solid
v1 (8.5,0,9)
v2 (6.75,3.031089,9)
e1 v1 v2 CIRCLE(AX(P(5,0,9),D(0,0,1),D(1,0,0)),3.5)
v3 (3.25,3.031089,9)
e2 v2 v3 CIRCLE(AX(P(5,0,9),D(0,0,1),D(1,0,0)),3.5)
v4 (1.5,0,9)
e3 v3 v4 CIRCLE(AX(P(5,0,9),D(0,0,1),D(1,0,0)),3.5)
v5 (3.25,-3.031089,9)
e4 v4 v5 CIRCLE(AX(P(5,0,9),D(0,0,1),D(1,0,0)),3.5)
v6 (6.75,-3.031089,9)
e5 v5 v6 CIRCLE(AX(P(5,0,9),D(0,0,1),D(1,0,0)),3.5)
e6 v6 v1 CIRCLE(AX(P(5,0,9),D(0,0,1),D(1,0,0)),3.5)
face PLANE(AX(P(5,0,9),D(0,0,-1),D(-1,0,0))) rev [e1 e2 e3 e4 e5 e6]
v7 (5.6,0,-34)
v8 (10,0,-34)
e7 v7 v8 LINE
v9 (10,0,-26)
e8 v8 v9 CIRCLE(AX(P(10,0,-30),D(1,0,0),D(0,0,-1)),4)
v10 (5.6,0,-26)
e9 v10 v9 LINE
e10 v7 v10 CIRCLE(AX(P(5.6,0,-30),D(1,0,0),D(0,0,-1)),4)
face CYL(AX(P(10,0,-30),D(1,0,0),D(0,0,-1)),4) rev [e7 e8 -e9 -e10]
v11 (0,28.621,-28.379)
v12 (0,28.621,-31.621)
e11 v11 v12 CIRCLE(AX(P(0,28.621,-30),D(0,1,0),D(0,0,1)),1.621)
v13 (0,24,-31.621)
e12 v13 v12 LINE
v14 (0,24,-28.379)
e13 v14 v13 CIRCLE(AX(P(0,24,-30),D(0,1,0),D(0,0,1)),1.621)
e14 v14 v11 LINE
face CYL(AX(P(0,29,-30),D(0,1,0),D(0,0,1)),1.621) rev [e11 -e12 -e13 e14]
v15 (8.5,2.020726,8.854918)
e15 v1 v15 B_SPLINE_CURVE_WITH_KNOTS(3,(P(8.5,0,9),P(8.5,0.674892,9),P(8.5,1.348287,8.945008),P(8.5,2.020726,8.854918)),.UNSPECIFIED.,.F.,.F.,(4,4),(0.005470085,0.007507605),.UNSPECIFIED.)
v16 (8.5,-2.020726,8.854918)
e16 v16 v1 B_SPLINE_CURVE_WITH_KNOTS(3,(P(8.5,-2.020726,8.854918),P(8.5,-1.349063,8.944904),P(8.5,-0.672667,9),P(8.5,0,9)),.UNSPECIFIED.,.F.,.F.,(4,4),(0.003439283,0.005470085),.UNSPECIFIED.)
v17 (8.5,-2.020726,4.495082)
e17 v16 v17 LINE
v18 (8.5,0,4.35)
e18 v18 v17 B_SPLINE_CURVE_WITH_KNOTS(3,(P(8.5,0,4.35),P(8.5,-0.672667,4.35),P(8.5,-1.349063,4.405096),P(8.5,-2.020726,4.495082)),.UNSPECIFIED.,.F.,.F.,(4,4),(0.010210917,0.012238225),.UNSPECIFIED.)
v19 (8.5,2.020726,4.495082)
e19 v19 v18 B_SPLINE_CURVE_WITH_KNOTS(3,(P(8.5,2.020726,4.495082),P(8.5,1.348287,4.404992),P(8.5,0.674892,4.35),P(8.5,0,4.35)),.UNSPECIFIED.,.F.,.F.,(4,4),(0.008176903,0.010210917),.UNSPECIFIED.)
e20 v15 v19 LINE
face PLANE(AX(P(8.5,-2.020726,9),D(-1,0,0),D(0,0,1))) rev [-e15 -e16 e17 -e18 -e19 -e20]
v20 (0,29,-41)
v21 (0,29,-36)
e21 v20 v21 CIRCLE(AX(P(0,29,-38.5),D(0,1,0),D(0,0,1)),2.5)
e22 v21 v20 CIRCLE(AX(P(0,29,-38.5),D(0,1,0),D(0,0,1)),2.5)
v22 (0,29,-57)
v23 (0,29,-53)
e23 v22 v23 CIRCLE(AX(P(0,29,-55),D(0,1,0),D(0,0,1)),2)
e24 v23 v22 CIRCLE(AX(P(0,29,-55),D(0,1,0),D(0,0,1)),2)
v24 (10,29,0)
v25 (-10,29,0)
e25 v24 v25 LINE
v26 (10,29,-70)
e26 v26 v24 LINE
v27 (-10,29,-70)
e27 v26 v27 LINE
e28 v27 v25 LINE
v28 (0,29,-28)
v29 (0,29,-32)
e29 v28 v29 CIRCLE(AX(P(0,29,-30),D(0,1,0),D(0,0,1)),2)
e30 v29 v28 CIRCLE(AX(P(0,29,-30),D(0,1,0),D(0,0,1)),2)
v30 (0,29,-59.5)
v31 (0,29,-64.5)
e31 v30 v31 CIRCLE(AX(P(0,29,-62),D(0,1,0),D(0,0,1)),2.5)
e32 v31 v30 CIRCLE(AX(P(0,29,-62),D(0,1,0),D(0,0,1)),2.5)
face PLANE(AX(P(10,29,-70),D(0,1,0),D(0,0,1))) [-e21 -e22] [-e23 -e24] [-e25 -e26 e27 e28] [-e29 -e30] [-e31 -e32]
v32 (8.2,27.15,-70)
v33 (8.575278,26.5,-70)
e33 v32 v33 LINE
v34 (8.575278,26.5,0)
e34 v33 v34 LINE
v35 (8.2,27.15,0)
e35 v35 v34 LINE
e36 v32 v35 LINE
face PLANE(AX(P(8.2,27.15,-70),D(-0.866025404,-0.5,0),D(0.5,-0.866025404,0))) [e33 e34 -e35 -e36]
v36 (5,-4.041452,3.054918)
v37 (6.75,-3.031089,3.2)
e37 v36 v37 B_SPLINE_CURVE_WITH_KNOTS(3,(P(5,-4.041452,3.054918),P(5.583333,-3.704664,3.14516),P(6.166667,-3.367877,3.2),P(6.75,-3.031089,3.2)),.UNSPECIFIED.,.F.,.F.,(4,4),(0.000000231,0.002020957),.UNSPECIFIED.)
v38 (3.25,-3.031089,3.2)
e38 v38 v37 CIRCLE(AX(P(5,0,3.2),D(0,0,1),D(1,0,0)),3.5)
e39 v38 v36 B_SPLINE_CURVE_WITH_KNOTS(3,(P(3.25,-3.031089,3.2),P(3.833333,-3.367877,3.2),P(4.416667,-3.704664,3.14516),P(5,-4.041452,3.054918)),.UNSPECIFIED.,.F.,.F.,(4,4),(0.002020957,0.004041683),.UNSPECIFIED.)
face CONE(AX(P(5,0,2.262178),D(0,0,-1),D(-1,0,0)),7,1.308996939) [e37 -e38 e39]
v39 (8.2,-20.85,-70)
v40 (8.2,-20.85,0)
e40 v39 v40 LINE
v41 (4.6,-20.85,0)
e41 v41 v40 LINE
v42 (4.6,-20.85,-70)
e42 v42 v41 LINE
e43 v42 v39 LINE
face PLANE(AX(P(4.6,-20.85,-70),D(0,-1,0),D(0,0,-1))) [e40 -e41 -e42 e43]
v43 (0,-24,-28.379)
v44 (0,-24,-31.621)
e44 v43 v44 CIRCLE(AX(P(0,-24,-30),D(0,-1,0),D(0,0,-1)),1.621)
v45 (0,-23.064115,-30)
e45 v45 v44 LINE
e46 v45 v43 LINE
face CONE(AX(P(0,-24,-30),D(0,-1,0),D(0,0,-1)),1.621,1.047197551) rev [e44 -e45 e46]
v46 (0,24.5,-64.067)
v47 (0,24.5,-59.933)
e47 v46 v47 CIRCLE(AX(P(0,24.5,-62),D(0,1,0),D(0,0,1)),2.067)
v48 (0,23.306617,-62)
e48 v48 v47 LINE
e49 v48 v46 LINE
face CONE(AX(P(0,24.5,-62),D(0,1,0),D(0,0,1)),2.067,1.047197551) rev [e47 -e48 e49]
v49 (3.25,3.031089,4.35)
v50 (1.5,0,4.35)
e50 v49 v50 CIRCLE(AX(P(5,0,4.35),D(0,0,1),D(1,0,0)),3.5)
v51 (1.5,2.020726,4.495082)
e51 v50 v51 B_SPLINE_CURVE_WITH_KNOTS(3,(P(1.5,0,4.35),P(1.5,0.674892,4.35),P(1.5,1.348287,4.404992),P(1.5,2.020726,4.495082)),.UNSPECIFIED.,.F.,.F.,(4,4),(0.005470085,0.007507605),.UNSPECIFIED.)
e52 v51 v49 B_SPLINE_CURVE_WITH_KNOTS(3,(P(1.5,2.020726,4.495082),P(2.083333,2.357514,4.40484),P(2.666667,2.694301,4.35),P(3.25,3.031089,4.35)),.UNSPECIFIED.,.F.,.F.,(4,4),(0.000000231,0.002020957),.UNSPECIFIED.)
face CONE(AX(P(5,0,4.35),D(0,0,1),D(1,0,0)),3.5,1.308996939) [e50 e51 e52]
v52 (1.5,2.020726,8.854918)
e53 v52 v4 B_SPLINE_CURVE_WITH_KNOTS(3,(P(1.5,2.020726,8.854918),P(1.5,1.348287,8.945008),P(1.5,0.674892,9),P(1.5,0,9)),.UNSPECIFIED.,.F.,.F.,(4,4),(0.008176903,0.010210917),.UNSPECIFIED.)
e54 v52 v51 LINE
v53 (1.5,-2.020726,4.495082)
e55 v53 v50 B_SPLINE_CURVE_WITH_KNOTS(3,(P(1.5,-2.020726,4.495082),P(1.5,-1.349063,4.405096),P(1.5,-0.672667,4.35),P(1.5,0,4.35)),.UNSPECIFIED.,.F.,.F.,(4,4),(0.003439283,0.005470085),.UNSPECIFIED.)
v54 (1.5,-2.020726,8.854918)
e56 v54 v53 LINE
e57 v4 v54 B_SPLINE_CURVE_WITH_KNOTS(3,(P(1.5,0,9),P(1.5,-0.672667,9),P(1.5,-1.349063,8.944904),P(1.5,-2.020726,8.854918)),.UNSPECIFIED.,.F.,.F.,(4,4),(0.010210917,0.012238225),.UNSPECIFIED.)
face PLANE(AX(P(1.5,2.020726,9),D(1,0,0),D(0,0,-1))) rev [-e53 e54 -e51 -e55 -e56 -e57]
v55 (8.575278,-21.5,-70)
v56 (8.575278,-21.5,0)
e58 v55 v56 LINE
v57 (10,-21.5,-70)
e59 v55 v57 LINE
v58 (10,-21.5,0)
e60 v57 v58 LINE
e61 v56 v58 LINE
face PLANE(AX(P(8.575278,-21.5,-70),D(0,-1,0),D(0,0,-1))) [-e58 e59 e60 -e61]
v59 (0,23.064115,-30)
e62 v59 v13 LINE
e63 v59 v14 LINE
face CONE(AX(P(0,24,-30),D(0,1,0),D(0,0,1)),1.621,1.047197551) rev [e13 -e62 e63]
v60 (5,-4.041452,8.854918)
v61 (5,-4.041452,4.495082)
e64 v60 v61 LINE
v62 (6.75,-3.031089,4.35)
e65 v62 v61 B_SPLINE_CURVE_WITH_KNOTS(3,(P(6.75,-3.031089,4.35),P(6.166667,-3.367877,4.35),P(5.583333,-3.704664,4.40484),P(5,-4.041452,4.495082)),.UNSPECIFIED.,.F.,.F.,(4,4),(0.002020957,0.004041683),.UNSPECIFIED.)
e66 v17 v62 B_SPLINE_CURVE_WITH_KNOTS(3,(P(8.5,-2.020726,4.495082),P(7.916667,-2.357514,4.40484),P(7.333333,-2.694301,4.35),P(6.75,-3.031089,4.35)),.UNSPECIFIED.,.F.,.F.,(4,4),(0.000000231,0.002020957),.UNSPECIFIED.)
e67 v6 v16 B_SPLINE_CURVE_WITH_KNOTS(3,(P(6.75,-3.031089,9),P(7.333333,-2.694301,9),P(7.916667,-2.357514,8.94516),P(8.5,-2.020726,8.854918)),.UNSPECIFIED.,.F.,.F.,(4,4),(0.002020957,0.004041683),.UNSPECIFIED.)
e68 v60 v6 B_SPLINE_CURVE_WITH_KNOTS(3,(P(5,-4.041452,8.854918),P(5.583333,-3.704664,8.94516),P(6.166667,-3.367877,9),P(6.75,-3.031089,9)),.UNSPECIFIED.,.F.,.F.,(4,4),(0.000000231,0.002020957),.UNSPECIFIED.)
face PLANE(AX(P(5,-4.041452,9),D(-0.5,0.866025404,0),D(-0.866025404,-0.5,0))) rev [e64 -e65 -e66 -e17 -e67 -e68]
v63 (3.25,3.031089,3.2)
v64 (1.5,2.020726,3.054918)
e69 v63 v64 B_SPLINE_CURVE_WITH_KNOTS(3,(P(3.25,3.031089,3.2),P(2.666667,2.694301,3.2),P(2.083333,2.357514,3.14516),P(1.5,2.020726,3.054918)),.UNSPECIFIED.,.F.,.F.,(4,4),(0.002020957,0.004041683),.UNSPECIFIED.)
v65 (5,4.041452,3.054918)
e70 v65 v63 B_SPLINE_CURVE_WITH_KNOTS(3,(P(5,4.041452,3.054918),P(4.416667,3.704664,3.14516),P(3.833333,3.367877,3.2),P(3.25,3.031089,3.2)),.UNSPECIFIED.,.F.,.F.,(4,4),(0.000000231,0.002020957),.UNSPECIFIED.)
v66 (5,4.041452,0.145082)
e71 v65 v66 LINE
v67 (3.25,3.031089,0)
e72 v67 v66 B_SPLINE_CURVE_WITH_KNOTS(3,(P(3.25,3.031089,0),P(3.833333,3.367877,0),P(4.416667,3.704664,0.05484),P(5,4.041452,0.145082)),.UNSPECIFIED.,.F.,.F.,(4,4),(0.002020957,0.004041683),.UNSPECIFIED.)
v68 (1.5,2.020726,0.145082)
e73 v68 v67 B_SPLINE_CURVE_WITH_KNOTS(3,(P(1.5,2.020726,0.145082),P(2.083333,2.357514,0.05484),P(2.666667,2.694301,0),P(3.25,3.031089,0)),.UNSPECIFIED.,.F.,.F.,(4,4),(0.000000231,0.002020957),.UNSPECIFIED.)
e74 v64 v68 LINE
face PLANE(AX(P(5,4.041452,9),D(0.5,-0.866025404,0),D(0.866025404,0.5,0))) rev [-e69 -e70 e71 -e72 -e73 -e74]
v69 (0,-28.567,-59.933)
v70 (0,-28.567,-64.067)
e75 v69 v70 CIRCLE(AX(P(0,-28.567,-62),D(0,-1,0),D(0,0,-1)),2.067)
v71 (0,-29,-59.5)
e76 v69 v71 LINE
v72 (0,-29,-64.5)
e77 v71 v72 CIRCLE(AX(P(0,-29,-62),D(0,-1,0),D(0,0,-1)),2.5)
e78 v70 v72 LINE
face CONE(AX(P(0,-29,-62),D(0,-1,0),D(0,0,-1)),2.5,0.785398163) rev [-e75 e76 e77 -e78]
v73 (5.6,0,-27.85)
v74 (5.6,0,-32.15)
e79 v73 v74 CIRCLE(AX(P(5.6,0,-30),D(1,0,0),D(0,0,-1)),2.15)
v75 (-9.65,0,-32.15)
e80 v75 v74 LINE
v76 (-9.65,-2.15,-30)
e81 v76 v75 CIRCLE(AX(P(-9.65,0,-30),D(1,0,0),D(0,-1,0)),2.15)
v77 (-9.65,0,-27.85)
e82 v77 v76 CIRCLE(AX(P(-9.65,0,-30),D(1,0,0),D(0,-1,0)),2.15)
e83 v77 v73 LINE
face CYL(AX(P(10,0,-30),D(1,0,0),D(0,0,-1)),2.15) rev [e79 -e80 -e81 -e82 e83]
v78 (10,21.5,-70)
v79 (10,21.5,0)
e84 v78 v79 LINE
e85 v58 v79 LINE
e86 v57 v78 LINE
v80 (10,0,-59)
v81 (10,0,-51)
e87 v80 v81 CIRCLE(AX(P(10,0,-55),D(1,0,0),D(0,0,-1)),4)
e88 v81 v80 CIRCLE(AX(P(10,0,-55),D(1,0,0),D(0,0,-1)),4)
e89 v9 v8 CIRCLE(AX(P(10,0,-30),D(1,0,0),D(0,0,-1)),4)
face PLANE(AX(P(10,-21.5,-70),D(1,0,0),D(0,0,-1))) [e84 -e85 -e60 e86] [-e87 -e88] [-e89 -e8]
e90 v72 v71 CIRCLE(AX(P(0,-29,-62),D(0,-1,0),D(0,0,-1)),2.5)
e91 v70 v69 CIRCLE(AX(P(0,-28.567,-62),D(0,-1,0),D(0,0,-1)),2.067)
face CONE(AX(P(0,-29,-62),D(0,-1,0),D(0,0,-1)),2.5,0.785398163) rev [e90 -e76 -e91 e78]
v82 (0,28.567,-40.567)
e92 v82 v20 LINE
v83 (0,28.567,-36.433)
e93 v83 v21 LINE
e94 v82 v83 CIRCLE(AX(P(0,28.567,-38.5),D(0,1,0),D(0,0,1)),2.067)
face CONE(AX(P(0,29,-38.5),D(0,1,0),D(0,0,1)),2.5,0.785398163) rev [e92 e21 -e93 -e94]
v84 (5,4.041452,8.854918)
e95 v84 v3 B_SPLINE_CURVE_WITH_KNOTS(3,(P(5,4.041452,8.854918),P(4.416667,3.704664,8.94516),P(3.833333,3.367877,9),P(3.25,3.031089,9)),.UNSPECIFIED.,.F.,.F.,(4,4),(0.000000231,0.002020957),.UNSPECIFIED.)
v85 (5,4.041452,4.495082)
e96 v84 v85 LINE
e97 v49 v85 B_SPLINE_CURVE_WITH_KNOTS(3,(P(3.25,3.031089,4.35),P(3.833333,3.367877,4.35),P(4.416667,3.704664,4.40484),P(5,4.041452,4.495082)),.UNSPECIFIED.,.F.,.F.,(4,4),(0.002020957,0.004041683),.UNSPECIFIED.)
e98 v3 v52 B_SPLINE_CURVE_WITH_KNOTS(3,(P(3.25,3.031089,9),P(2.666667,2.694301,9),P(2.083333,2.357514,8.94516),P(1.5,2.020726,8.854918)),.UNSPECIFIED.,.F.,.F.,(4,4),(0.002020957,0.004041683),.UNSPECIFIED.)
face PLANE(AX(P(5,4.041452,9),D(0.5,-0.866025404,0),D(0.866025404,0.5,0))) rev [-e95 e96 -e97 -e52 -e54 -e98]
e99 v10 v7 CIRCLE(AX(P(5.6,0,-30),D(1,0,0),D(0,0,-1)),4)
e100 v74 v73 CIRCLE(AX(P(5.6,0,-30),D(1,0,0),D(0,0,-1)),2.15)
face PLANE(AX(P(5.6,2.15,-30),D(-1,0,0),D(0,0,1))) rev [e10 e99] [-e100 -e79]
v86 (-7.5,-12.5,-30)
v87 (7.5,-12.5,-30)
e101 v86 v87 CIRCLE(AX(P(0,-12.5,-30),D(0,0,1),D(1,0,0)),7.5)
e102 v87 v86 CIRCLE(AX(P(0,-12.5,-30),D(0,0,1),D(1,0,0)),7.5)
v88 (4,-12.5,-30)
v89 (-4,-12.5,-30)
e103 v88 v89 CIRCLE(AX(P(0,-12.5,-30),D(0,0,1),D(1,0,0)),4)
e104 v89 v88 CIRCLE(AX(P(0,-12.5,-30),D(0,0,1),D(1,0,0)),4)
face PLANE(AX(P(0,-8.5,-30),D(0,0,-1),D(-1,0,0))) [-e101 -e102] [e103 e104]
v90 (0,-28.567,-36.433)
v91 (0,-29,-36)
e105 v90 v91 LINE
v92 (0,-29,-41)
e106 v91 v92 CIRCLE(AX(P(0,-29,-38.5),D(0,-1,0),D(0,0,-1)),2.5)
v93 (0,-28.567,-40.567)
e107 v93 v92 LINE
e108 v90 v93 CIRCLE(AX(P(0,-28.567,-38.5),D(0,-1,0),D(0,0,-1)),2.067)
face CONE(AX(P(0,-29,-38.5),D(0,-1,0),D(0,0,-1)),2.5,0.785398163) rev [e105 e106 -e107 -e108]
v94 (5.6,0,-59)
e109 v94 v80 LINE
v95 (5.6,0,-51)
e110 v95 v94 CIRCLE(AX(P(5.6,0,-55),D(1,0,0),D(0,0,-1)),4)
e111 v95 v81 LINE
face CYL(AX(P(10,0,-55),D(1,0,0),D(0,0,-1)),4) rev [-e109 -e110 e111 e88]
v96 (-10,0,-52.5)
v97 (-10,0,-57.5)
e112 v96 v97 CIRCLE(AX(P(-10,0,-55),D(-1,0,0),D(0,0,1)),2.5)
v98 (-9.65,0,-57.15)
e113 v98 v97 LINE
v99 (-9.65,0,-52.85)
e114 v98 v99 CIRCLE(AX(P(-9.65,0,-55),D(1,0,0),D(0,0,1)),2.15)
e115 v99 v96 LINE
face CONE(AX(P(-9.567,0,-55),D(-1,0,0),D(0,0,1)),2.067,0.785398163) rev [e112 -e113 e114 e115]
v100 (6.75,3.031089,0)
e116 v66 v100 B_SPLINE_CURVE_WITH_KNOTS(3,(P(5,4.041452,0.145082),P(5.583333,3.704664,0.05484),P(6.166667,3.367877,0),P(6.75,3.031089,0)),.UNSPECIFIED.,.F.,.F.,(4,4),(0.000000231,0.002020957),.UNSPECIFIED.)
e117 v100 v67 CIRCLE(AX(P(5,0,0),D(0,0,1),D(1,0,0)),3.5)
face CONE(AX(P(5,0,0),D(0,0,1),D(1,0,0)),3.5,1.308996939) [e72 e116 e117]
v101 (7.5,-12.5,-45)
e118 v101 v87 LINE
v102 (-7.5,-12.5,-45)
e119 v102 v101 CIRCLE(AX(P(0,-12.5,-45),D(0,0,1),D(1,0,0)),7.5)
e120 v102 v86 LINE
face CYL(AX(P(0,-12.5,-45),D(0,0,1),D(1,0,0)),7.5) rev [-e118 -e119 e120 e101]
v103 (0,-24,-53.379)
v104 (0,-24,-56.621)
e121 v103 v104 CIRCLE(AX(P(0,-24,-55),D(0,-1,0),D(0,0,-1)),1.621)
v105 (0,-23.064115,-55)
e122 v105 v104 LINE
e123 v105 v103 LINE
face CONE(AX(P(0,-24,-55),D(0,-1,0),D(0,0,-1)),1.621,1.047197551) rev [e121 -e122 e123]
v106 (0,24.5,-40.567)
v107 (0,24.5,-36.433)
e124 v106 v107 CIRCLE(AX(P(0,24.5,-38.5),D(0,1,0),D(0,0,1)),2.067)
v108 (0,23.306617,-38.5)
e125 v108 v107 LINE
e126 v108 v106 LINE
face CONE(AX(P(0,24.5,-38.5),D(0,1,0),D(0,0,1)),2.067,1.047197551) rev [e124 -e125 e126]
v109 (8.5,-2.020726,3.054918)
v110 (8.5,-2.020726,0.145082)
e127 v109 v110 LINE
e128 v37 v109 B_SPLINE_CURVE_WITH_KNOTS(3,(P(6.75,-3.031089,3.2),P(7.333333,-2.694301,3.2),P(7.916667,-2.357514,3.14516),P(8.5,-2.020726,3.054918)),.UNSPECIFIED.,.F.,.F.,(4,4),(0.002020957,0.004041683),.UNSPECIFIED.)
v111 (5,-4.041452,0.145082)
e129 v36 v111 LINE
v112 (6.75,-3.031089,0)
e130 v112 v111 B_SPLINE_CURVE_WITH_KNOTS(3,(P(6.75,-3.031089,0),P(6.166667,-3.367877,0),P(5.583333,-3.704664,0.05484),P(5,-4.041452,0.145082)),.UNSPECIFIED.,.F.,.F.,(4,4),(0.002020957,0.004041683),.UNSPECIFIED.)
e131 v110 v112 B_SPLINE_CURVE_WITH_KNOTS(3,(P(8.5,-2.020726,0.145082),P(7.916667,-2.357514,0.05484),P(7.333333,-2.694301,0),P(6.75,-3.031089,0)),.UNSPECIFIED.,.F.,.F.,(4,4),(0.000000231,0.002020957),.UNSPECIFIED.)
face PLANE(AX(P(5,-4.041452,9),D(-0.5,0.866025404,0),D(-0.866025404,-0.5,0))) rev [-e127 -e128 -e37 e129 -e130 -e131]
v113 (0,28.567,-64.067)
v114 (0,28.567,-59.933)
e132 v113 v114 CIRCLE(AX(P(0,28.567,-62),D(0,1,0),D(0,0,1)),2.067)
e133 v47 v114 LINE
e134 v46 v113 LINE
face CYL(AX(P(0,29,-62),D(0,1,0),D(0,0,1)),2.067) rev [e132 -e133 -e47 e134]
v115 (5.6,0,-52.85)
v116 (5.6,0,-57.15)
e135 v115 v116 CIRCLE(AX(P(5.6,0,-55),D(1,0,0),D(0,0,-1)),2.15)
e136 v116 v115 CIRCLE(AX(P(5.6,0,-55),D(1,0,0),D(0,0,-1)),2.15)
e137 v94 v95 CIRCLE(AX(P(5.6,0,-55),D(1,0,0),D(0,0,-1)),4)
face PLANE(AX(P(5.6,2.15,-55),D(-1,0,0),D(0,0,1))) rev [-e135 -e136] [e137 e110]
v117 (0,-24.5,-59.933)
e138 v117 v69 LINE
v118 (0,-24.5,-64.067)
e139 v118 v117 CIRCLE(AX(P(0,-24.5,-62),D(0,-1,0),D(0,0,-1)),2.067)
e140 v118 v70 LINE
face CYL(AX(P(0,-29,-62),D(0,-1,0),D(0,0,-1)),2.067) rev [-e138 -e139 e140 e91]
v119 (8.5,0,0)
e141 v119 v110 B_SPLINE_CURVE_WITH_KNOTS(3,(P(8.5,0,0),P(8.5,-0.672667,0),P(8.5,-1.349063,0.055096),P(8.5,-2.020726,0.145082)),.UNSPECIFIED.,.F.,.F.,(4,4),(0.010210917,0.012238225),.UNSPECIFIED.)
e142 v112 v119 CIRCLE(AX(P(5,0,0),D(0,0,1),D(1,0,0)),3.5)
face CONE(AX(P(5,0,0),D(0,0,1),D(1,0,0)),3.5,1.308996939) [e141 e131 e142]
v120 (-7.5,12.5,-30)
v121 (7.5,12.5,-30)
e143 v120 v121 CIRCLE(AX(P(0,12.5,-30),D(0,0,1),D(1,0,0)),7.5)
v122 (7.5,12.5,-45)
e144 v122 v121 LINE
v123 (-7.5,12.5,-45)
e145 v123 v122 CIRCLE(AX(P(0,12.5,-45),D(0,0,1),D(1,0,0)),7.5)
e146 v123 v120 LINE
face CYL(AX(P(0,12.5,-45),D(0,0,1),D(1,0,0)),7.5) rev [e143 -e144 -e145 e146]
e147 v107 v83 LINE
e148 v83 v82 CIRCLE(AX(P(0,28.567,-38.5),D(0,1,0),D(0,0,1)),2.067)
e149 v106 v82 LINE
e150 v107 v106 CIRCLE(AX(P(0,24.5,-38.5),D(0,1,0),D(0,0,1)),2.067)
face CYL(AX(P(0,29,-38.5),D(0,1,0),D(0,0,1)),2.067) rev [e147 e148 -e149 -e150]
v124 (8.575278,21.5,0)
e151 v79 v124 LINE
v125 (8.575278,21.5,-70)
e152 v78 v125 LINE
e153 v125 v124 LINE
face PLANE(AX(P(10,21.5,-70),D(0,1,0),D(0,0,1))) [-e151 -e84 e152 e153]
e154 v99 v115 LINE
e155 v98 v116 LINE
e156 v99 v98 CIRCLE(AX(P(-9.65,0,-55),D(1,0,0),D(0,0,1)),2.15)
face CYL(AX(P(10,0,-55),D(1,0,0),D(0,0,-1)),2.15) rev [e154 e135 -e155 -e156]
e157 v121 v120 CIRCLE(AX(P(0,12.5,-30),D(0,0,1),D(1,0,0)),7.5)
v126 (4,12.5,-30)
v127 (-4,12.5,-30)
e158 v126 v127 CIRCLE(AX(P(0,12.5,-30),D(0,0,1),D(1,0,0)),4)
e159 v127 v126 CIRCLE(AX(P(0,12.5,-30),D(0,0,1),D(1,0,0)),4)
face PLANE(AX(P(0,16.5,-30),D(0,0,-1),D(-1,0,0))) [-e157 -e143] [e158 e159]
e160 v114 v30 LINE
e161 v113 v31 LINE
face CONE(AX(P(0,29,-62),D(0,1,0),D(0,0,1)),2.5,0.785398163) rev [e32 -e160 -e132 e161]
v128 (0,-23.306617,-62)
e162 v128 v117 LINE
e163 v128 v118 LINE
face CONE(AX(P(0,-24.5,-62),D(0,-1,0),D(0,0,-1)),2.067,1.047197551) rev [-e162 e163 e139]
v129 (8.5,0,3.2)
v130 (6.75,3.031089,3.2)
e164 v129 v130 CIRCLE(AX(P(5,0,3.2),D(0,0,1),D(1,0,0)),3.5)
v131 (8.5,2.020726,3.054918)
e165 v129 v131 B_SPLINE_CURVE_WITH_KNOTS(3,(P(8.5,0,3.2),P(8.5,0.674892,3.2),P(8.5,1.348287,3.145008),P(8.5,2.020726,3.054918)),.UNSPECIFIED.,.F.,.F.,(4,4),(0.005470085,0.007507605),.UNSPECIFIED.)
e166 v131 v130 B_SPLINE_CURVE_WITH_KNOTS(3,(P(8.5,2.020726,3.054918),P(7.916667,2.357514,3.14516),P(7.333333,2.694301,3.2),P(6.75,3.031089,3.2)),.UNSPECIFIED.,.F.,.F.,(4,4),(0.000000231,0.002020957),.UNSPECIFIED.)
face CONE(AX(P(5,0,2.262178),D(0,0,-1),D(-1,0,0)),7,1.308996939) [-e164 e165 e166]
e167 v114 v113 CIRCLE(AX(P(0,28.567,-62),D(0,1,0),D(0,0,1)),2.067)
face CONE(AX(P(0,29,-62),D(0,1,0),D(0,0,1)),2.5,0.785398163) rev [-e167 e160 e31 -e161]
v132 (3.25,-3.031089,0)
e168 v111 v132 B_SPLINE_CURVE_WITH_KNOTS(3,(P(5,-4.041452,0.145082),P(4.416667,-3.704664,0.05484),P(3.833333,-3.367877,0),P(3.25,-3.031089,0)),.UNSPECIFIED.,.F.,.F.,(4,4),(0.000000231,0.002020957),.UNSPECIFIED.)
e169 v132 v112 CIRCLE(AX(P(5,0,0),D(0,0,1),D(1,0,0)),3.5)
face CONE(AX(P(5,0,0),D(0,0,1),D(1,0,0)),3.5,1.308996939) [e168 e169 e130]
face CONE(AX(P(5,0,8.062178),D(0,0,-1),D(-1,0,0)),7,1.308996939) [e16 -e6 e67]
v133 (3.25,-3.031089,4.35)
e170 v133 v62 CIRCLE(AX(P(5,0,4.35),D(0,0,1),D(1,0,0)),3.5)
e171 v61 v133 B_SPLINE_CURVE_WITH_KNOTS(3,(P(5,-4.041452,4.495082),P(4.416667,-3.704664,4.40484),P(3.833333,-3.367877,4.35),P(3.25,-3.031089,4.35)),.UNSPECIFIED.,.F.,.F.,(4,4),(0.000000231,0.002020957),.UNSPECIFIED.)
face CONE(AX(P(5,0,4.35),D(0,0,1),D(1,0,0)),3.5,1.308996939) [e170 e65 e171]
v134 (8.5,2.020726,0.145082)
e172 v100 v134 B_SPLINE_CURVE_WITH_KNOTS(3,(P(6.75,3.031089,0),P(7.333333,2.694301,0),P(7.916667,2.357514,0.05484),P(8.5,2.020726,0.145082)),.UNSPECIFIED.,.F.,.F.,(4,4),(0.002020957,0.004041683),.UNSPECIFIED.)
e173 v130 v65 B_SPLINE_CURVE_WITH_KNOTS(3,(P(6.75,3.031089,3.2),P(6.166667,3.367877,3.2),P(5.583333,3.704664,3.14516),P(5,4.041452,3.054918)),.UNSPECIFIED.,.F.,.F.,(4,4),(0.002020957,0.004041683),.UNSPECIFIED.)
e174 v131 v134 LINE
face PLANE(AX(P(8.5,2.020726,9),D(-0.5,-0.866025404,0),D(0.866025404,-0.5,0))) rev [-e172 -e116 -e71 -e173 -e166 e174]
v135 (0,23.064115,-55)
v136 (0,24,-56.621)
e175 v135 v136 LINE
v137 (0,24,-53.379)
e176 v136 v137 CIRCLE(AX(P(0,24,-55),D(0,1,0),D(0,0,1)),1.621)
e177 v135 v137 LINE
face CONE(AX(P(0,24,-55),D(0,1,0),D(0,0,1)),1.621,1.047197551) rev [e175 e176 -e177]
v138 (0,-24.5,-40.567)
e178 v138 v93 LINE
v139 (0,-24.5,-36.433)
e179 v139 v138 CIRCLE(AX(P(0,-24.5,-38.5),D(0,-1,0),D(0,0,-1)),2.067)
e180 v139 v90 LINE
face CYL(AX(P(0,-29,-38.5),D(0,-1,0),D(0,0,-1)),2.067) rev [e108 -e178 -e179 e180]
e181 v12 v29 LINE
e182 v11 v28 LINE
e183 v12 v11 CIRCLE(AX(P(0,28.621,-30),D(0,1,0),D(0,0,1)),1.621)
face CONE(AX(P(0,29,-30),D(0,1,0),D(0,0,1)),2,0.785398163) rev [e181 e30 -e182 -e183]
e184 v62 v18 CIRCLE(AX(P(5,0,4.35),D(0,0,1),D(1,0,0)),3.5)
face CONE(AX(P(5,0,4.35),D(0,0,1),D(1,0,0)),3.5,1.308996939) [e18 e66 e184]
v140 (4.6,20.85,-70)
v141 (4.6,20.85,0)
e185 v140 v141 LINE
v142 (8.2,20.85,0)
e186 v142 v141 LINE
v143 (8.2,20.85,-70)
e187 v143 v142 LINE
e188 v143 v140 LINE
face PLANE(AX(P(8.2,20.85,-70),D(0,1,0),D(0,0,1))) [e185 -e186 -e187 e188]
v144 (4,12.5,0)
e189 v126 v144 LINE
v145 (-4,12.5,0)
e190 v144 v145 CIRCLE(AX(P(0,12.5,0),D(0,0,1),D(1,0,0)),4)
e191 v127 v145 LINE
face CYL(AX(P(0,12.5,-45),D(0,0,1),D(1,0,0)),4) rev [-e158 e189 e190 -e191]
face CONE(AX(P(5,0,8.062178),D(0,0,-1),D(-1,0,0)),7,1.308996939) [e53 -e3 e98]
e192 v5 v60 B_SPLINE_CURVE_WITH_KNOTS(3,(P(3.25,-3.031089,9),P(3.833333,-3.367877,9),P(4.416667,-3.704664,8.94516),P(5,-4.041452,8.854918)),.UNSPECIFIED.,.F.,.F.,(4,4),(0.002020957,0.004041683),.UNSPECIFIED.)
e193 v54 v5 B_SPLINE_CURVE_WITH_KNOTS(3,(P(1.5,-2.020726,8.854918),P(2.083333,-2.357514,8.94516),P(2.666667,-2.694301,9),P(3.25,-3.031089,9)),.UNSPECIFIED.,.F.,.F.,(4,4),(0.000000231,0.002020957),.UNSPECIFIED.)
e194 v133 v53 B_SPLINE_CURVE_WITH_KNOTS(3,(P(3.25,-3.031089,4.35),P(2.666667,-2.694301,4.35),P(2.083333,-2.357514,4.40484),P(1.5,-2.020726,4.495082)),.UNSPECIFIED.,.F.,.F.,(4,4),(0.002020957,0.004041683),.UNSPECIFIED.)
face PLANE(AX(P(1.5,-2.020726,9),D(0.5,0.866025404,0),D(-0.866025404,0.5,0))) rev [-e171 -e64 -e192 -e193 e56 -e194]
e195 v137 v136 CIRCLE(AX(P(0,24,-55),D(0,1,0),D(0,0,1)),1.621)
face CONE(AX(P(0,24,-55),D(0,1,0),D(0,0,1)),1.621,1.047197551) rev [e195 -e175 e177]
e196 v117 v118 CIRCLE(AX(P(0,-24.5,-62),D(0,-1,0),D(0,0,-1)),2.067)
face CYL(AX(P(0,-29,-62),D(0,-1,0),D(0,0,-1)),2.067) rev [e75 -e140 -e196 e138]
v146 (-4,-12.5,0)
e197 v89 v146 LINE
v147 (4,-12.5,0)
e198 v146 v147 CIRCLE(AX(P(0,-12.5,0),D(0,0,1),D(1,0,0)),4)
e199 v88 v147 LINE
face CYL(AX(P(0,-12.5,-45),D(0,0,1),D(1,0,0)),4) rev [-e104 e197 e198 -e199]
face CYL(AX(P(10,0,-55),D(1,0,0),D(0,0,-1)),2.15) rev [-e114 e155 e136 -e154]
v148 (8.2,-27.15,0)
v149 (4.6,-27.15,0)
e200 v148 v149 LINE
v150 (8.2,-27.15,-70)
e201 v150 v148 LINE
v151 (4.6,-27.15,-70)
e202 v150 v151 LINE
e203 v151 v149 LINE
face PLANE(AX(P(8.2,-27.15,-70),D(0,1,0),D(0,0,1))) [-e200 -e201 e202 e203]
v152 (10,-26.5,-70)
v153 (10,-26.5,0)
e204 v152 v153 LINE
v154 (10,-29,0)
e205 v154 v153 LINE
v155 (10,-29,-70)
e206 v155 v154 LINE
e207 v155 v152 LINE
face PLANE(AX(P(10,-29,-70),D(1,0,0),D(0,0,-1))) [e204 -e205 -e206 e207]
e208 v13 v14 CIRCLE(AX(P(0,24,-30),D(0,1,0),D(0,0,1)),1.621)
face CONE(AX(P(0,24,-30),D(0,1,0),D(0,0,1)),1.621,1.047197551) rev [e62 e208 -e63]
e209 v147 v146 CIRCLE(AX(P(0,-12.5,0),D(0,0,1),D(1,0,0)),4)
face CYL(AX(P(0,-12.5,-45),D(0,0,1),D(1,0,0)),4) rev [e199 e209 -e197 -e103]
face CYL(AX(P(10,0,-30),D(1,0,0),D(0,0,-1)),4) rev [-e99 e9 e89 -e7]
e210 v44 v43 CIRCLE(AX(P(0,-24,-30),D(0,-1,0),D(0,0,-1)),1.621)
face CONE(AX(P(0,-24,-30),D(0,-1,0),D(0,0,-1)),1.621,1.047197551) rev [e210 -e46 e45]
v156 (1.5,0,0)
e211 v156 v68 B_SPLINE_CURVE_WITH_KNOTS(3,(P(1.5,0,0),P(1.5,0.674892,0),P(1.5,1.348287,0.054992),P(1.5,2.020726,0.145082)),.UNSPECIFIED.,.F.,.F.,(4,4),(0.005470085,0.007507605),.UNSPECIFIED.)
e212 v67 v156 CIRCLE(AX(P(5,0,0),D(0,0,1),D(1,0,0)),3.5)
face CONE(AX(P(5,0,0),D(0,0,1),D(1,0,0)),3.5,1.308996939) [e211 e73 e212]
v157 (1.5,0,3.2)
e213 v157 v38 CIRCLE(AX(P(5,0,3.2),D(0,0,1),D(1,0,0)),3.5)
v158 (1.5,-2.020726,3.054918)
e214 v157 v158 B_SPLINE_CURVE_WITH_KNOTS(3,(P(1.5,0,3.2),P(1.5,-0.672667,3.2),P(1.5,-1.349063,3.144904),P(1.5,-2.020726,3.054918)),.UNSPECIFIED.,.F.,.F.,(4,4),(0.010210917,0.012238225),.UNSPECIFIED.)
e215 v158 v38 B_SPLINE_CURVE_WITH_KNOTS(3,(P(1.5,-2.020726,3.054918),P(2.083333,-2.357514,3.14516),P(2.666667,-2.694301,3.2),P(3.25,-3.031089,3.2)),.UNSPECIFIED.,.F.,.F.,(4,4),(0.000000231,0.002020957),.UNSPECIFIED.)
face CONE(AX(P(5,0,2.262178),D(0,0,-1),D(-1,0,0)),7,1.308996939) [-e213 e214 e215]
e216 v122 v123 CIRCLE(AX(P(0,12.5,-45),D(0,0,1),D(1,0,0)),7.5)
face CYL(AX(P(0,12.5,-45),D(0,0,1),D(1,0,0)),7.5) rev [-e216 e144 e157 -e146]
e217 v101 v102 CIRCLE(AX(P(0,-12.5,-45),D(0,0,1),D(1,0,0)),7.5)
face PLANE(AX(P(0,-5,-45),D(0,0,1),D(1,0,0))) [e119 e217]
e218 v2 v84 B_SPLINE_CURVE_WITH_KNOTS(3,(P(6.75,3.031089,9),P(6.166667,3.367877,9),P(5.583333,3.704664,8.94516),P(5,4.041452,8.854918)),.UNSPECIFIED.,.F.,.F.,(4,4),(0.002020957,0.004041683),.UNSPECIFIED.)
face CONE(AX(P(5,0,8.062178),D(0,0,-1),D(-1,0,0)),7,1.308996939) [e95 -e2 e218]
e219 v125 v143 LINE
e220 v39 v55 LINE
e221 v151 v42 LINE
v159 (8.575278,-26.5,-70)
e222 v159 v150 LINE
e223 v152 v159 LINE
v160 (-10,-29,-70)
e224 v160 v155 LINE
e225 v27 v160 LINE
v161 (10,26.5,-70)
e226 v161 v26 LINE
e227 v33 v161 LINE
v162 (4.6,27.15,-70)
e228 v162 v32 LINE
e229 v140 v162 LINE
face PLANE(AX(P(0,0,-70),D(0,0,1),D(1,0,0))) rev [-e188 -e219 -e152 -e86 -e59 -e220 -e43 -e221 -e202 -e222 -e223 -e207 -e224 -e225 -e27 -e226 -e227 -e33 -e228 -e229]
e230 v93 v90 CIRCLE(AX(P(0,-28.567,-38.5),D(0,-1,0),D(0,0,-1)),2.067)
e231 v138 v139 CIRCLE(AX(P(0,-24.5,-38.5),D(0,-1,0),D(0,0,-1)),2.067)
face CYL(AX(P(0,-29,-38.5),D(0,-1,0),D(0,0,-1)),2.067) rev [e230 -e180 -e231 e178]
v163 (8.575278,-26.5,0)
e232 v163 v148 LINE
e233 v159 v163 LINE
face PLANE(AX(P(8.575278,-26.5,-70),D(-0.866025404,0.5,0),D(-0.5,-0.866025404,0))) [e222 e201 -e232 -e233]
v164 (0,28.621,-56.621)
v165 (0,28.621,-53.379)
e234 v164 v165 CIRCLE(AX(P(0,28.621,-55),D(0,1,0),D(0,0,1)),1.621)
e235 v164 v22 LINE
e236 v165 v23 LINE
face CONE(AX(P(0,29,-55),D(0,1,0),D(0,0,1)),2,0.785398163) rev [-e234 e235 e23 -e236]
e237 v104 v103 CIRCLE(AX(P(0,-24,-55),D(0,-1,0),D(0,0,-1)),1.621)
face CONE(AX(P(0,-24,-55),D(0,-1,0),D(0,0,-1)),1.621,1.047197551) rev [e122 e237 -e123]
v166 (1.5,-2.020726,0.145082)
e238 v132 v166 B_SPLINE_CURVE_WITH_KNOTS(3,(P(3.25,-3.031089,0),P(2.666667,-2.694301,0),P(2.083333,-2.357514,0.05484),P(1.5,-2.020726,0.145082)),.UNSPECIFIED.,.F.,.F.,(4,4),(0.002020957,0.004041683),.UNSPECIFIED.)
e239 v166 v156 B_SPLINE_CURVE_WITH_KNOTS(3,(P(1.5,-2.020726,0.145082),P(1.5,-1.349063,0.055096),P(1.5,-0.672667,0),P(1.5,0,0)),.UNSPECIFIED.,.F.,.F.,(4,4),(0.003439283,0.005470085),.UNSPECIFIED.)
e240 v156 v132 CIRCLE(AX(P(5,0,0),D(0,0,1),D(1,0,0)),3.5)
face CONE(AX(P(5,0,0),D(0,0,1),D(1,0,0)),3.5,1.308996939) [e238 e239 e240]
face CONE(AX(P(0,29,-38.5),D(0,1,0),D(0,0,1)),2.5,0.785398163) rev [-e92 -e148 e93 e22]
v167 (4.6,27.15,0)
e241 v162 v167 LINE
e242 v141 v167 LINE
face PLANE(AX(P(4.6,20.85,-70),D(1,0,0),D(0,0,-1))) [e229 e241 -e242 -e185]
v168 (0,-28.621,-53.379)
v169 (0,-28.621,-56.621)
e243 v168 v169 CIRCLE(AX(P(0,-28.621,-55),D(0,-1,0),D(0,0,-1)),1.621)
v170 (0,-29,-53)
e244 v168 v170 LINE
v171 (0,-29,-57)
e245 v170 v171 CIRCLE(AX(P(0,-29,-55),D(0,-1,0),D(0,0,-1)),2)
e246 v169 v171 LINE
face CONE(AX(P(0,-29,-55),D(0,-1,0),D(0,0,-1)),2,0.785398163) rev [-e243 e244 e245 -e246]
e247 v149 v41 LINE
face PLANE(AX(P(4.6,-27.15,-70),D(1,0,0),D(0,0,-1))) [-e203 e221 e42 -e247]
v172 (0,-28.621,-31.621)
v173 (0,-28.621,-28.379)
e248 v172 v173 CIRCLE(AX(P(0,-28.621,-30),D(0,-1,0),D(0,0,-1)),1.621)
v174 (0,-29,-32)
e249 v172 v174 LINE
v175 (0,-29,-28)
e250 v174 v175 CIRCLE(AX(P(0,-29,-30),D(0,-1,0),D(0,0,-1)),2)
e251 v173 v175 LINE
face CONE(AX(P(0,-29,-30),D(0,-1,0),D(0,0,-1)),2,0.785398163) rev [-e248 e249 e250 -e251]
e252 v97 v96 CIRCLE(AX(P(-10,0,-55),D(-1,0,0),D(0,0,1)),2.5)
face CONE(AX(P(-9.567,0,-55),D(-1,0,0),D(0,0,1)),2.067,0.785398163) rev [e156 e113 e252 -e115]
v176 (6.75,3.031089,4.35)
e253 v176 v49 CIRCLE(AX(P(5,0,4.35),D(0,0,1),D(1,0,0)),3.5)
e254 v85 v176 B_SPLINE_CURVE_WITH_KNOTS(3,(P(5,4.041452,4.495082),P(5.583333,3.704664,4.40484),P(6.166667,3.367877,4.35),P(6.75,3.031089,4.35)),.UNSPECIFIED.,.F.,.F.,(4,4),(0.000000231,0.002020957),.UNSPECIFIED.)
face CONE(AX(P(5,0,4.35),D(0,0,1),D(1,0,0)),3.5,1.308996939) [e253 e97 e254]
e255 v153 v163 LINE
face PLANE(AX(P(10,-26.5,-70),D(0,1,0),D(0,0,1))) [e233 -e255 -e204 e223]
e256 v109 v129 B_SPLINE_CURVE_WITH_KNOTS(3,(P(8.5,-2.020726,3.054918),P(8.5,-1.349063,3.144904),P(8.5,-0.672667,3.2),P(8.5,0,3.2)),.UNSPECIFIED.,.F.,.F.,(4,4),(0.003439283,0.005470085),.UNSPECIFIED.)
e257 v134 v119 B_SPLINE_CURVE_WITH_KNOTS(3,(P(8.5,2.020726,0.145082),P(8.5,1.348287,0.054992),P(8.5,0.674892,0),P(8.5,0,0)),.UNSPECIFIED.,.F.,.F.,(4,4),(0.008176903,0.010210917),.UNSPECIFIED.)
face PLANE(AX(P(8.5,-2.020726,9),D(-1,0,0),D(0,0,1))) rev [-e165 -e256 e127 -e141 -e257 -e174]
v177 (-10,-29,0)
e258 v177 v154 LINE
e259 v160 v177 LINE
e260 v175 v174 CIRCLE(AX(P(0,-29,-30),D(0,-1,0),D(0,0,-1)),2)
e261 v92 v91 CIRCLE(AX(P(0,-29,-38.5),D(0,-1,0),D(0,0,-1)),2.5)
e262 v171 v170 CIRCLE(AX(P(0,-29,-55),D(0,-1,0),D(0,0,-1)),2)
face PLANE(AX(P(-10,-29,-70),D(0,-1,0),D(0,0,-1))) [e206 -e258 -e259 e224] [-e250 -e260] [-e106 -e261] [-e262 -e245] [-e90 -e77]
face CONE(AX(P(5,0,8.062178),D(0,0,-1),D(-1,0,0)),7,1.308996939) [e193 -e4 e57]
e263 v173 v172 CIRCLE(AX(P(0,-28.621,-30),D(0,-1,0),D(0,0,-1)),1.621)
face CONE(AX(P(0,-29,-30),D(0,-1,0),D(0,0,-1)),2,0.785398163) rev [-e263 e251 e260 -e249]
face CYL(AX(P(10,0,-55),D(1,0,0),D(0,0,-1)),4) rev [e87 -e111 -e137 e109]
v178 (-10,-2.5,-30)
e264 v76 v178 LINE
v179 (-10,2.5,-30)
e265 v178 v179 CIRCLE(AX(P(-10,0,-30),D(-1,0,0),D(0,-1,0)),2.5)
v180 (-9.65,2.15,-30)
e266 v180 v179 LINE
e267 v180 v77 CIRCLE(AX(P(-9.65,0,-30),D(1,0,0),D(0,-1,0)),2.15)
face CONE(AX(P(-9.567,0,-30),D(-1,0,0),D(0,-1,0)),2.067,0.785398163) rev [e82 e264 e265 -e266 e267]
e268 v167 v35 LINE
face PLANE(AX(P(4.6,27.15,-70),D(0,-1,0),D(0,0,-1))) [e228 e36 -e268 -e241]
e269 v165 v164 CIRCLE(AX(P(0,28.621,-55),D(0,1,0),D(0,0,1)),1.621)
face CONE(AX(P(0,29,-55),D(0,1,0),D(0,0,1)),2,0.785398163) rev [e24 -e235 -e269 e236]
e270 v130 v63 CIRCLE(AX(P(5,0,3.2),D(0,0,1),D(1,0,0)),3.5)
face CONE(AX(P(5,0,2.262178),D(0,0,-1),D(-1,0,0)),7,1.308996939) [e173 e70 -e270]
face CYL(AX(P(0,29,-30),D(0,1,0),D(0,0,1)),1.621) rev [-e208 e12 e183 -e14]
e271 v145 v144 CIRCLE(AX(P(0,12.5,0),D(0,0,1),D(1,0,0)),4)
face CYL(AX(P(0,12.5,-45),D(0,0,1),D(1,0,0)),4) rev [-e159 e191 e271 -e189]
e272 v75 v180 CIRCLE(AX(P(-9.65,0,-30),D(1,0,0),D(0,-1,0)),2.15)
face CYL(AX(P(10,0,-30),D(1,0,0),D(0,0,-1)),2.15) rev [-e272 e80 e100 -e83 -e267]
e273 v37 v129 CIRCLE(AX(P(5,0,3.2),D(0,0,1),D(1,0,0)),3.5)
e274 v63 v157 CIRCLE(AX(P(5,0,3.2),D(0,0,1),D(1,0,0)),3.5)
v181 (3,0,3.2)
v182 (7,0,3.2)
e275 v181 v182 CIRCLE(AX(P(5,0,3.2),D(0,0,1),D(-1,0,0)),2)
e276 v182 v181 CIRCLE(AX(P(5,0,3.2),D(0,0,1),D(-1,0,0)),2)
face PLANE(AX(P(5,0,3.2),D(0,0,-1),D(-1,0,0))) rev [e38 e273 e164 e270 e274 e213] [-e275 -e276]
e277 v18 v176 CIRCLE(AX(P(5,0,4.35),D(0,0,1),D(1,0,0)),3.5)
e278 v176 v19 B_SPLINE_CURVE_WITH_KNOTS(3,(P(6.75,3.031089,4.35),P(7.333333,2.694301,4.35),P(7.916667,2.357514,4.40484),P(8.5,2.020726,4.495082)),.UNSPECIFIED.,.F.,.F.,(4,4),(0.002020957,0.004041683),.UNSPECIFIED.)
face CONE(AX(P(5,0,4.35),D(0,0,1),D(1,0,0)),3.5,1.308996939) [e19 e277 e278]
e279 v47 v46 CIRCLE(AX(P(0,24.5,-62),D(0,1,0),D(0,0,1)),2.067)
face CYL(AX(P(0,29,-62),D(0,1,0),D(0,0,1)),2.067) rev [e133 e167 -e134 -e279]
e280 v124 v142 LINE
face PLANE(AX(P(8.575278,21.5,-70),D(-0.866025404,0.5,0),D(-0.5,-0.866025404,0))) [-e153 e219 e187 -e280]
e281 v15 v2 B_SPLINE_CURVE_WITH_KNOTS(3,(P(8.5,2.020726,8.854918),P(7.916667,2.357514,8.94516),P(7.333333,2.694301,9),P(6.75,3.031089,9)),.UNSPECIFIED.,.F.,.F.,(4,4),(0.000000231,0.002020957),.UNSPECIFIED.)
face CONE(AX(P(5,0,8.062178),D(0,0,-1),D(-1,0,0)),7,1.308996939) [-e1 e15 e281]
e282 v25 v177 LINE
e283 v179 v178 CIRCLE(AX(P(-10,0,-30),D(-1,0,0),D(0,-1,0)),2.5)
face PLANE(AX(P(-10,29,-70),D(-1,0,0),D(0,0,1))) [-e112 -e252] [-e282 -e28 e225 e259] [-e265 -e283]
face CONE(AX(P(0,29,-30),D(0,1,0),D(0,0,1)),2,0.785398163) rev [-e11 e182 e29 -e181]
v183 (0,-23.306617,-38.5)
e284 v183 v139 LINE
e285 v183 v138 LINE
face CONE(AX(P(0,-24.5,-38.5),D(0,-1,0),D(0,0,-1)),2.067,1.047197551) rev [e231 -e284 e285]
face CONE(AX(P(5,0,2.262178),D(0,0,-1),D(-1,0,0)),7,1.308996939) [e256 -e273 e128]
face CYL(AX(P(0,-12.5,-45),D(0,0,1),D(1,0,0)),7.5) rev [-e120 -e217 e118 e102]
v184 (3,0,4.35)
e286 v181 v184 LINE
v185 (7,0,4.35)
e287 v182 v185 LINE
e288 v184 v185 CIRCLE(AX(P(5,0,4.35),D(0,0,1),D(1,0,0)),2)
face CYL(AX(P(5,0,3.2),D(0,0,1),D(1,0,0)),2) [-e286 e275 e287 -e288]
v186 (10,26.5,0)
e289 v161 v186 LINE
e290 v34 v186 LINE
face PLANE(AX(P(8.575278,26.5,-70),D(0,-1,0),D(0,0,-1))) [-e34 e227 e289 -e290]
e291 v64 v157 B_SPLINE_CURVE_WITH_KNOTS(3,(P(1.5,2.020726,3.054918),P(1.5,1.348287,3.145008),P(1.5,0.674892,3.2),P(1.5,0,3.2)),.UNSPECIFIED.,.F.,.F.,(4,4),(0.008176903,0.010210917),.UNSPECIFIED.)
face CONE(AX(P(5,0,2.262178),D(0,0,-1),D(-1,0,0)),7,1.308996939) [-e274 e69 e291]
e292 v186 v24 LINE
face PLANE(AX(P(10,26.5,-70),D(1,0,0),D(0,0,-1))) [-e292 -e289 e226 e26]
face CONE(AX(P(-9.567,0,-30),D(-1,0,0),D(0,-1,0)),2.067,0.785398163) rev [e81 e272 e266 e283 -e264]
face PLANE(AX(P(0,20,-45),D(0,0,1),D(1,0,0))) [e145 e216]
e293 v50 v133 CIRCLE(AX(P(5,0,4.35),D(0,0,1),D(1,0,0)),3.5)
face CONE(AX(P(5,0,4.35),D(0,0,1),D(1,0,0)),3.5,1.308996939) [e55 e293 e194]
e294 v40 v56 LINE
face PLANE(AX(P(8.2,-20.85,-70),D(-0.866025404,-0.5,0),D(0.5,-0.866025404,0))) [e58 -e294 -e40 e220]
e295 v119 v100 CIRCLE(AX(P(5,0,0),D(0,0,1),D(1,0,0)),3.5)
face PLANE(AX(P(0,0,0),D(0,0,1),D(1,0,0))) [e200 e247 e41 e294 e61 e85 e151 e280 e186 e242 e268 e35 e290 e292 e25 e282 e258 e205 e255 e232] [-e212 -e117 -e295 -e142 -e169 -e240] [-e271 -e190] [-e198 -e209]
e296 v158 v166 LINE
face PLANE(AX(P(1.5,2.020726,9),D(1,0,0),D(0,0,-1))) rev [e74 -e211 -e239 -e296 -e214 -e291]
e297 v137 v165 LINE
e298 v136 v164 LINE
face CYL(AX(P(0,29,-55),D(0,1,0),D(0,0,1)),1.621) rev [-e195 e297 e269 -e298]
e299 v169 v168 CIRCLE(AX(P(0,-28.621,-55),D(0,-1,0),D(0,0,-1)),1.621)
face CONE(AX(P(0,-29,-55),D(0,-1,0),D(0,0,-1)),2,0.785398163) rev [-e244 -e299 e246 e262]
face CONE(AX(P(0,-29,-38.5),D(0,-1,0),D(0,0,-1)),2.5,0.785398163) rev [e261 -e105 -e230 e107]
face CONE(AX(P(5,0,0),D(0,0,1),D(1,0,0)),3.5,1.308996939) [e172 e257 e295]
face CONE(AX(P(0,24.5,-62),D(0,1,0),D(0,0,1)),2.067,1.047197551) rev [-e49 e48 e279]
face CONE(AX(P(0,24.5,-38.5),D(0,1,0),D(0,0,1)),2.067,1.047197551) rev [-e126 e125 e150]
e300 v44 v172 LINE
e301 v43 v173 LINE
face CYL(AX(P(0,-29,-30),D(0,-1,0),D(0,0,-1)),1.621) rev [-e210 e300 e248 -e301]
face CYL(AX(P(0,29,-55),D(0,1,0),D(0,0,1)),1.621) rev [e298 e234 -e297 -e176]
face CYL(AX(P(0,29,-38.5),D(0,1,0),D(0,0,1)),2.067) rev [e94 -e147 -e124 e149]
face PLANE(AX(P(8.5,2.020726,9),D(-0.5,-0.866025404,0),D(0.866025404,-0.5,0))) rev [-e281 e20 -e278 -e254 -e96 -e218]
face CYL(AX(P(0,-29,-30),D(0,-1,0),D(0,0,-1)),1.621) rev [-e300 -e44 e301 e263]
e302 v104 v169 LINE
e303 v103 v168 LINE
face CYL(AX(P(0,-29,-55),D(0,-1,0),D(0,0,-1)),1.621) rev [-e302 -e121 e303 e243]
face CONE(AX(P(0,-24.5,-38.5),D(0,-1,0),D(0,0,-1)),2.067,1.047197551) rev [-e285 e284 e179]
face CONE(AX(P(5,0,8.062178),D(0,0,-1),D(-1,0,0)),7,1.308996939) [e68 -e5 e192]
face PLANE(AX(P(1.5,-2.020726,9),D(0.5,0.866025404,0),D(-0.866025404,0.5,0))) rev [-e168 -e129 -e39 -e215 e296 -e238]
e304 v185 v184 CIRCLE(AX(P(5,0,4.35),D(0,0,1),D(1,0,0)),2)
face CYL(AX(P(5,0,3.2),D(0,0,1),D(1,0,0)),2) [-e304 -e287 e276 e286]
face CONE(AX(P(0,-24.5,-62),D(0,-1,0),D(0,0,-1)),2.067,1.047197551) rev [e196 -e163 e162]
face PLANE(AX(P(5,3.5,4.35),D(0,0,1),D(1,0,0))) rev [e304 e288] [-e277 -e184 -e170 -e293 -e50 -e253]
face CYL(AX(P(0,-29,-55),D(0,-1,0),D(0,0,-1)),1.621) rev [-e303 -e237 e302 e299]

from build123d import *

# Parameters (mm, degrees)
BOSS_EXTRUDE1_DEPTH = 70
HOLE1_D             = 4.3
HOLE1_CBORE_D       = 8
HOLE1_CBORE_DEPTH   = 4.4
HOLE2_D             = 4.3
HOLE2_CBORE_D       = 8
HOLE2_CBORE_DEPTH   = 4.4
HOLE3_D             = 4.134
HOLE3_DEPTH         = 4.5
HOLE3_CSINK_D       = 5
HOLE3_CSINK_ANGLE   = 90
HOLE3_TIP           = 1.193383006
HOLE4_D             = 4.134
HOLE4_DEPTH         = 4.5
HOLE4_CSINK_D       = 5
HOLE4_CSINK_ANGLE   = 90
HOLE4_TIP           = 1.193383006
HOLE5_D             = 4.134
HOLE5_DEPTH         = 4.5
HOLE5_CSINK_D       = 5
HOLE5_CSINK_ANGLE   = 90
HOLE5_TIP           = 1.193383006
HOLE6_D             = 4.134
HOLE6_DEPTH         = 4.5
HOLE6_CSINK_D       = 5
HOLE6_CSINK_ANGLE   = 90
HOLE6_TIP           = 1.193383006
HOLE7_D             = 3.242
HOLE7_DEPTH         = 5
HOLE7_CSINK_D       = 4
HOLE7_CSINK_ANGLE   = 90
HOLE7_TIP           = 0.935884786
HOLE8_D             = 3.242
HOLE8_DEPTH         = 5
HOLE8_CSINK_D       = 4
HOLE8_CSINK_ANGLE   = 90
HOLE8_TIP           = 0.935884786
HOLE9_D             = 3.242
HOLE9_DEPTH         = 5
HOLE9_CSINK_D       = 4
HOLE9_CSINK_ANGLE   = 90
HOLE9_TIP           = 0.935884786
HOLE10_D            = 3.242
HOLE10_DEPTH        = 5
HOLE10_CSINK_D      = 4
HOLE10_CSINK_ANGLE  = 90
HOLE10_TIP          = 0.935884786
SKETCH28_R          = 8
CUT_EXTRUDE1_DEPTH  = 9


with BuildPart() as part:
    # Sketch1 → Boss-Extrude1 (new body)
    with BuildSketch(Plane.XY):
        Polygon((-10, 29), (-10, -29), (10, -29), (10, -26.5), (8.575277675, -26.5), (8.2, -27.15), (4.6, -27.15), (4.6, -20.85), (8.2, -20.85), (8.575277675, -21.5), (10, -21.5), (10, 21.5), (8.575277675, 21.5), (8.2, 20.85), (4.6, 20.85), (4.6, 27.15), (8.2, 27.15), (8.575277675, 26.5), (10, 26.5), (10, 29), align=None)
    extrude(amount=-BOSS_EXTRUDE1_DEPTH)

    # Sketch2 → Cut-Revolve1 (revolve, cut)
    with BuildSketch(Plane(origin=(0, 0, 0), x_dir=(0, 0, -1), z_dir=(1, 0, 0)), mode=Mode.PRIVATE) as cut_revolve1_sk:
        Polygon((0, 12.5), (0, 16.5), (30, 16.5), (30, 20), (45, 20), (45, 12.5), align=None)
    revolve(cut_revolve1_sk.sketch.rotate(Axis((0, 12.5, -45), (0, 0, 1)), 270), axis=Axis((0, 12.5, -45), (0, 0, 1)), mode=Mode.SUBTRACT)

    # Sketch3 → Cut-Revolve2 (revolve, cut)
    with BuildSketch(Plane(origin=(0, 0, 0), x_dir=(0, 0, -1), z_dir=(1, 0, 0)), mode=Mode.PRIVATE) as cut_revolve2_sk:
        Polygon((0, -12.5), (0, -8.5), (30, -8.5), (30, -5), (45, -5), (45, -12.5), align=None)
    revolve(cut_revolve2_sk.sketch.rotate(Axis((0, -12.5, -45), (0, 0, 1)), 270), axis=Axis((0, -12.5, -45), (0, 0, 1)), mode=Mode.SUBTRACT)

    # Hole1 (through all)
    with Locations(Plane(origin=(10, 0, 0), x_dir=(0, 0, -1), z_dir=(1, 0, 0))):
        with Locations((30, 0)):
            CounterBoreHole(HOLE1_D / 2, HOLE1_CBORE_D / 2, HOLE1_CBORE_DEPTH)

    # Hole2 (through all)
    with Locations(Plane(origin=(10, 0, 0), x_dir=(0, 0, -1), z_dir=(1, 0, 0))):
        with Locations((55, 0)):
            CounterBoreHole(HOLE2_D / 2, HOLE2_CBORE_D / 2, HOLE2_CBORE_DEPTH)

    # Sketch8 → Cut-Revolve3 (revolve, cut)
    with BuildSketch(Plane.XY.offset(-30), mode=Mode.PRIVATE) as cut_revolve3_sk:
        Polygon((-10, 0), (-10, 2.5), (-9.567, 2.067), (-2, 2.067), (-0.806616994, 0), align=None)
    revolve(cut_revolve3_sk.sketch.rotate(Axis((-0.806616994, 0, -30), (-1, 0, 0)), 90), axis=Axis((-0.806616994, 0, -30), (-1, 0, 0)), mode=Mode.SUBTRACT)

    # Sketch9 → Cut-Revolve4 (revolve, cut)
    with BuildSketch(Plane.XY.offset(-55), mode=Mode.PRIVATE) as cut_revolve4_sk:
        Polygon((-10, 0), (-10, 2.5), (-9.567, 2.067), (-2, 2.067), (-0.806616994, 0), align=None)
    revolve(cut_revolve4_sk.sketch.rotate(Axis((-0.806616994, 0, -55), (-1, 0, 0)), 90), axis=Axis((-0.806616994, 0, -55), (-1, 0, 0)), mode=Mode.SUBTRACT)

    # Hole3
    with Locations(Plane(origin=(0, 29, 0), x_dir=(1, 0, 0), z_dir=(0, 1, 0))):
        with Locations((0, 38.5)):
            CounterSinkHole(HOLE3_D / 2, HOLE3_CSINK_D / 2, depth=HOLE3_DEPTH, counter_sink_angle=HOLE3_CSINK_ANGLE)
            with Locations((0, 0, -(HOLE3_DEPTH + HOLE3_TIP / 2))):  # 120° drill point
                Cone(0, HOLE3_D / 2, HOLE3_TIP, mode=Mode.SUBTRACT)

    # Hole4
    with Locations(Plane(origin=(0, 29, 0), x_dir=(1, 0, 0), z_dir=(0, 1, 0))):
        with Locations((0, 62)):
            CounterSinkHole(HOLE4_D / 2, HOLE4_CSINK_D / 2, depth=HOLE4_DEPTH, counter_sink_angle=HOLE4_CSINK_ANGLE)
            with Locations((0, 0, -(HOLE4_DEPTH + HOLE4_TIP / 2))):  # 120° drill point
                Cone(0, HOLE4_D / 2, HOLE4_TIP, mode=Mode.SUBTRACT)

    # Hole5
    with Locations(Plane(origin=(0, -29, 0), x_dir=(-1, 0, 0), z_dir=(0, -1, 0))):
        with Locations((0, 38.5)):
            CounterSinkHole(HOLE5_D / 2, HOLE5_CSINK_D / 2, depth=HOLE5_DEPTH, counter_sink_angle=HOLE5_CSINK_ANGLE)
            with Locations((0, 0, -(HOLE5_DEPTH + HOLE5_TIP / 2))):  # 120° drill point
                Cone(0, HOLE5_D / 2, HOLE5_TIP, mode=Mode.SUBTRACT)

    # Hole6
    with Locations(Plane(origin=(0, -29, 0), x_dir=(-1, 0, 0), z_dir=(0, -1, 0))):
        with Locations((0, 62)):
            CounterSinkHole(HOLE6_D / 2, HOLE6_CSINK_D / 2, depth=HOLE6_DEPTH, counter_sink_angle=HOLE6_CSINK_ANGLE)
            with Locations((0, 0, -(HOLE6_DEPTH + HOLE6_TIP / 2))):  # 120° drill point
                Cone(0, HOLE6_D / 2, HOLE6_TIP, mode=Mode.SUBTRACT)

    # Hole7
    with Locations(Plane(origin=(0, 29, 0), x_dir=(1, 0, 0), z_dir=(0, 1, 0))):
        with Locations((0, 30)):
            CounterSinkHole(HOLE7_D / 2, HOLE7_CSINK_D / 2, depth=HOLE7_DEPTH, counter_sink_angle=HOLE7_CSINK_ANGLE)
            with Locations((0, 0, -(HOLE7_DEPTH + HOLE7_TIP / 2))):  # 120° drill point
                Cone(0, HOLE7_D / 2, HOLE7_TIP, mode=Mode.SUBTRACT)

    # Hole8
    with Locations(Plane(origin=(0, 29, 0), x_dir=(1, 0, 0), z_dir=(0, 1, 0))):
        with Locations((0, 55)):
            CounterSinkHole(HOLE8_D / 2, HOLE8_CSINK_D / 2, depth=HOLE8_DEPTH, counter_sink_angle=HOLE8_CSINK_ANGLE)
            with Locations((0, 0, -(HOLE8_DEPTH + HOLE8_TIP / 2))):  # 120° drill point
                Cone(0, HOLE8_D / 2, HOLE8_TIP, mode=Mode.SUBTRACT)

    # Hole9
    with Locations(Plane(origin=(0, -29, 0), x_dir=(-1, 0, 0), z_dir=(0, -1, 0))):
        with Locations((0, 30)):
            CounterSinkHole(HOLE9_D / 2, HOLE9_CSINK_D / 2, depth=HOLE9_DEPTH, counter_sink_angle=HOLE9_CSINK_ANGLE)
            with Locations((0, 0, -(HOLE9_DEPTH + HOLE9_TIP / 2))):  # 120° drill point
                Cone(0, HOLE9_D / 2, HOLE9_TIP, mode=Mode.SUBTRACT)

    # Hole10
    with Locations(Plane(origin=(0, -29, 0), x_dir=(-1, 0, 0), z_dir=(0, -1, 0))):
        with Locations((0, 55)):
            CounterSinkHole(HOLE10_D / 2, HOLE10_CSINK_D / 2, depth=HOLE10_DEPTH, counter_sink_angle=HOLE10_CSINK_ANGLE)
            with Locations((0, 0, -(HOLE10_DEPTH + HOLE10_TIP / 2))):  # 120° drill point
                Cone(0, HOLE10_D / 2, HOLE10_TIP, mode=Mode.SUBTRACT)

    # Sketch26 → Revolve1 (revolve)
    with BuildSketch(Plane(origin=(5, 0, 0), x_dir=(0, 0, -1), z_dir=(1, 0, 0)), mode=Mode.PRIVATE) as revolve1_sk:
        Polygon((-3.2, 0), (-3.2, 3.5), (-2.262177826, 7), (-0.937822174, 7), (0, 3.5), (0, 0), align=None)
    revolve(revolve1_sk.sketch.rotate(Axis((5, 0, 0), (0, 0, 1)), 270), axis=Axis((5, 0, 0), (0, 0, 1)))

    # Sketch27 → Revolve2 (revolve)
    with BuildSketch(Plane(origin=(5, 0, 0), x_dir=(0, 0, -1), z_dir=(1, 0, 0)), mode=Mode.PRIVATE) as revolve2_sk:
        Polygon((-9, 0), (-9, 3.5), (-8.062177826, 7), (-5.287822174, 7), (-4.35, 3.5), (-4.35, 2), (-3.2, 2), (-3.2, 0), align=None)
    revolve(revolve2_sk.sketch.rotate(Axis((5, 0, 3.2), (0, 0, 1)), 270), axis=Axis((5, 0, 3.2), (0, 0, 1)))

    # Sketch28 → Cut-Extrude1 (cut)
    with BuildSketch(Plane.XY):
        with Locations((5, 0)):
            Circle(SKETCH28_R)
        Polygon((1.5, 2.020725942), (1.5, -2.020725942), (5, -4.041451884), (8.5, -2.020725942), (8.5, 2.020725942), (5, 4.041451884), align=None, mode=Mode.SUBTRACT)
    extrude(amount=CUT_EXTRUDE1_DEPTH, mode=Mode.SUBTRACT)


solid = part.part
